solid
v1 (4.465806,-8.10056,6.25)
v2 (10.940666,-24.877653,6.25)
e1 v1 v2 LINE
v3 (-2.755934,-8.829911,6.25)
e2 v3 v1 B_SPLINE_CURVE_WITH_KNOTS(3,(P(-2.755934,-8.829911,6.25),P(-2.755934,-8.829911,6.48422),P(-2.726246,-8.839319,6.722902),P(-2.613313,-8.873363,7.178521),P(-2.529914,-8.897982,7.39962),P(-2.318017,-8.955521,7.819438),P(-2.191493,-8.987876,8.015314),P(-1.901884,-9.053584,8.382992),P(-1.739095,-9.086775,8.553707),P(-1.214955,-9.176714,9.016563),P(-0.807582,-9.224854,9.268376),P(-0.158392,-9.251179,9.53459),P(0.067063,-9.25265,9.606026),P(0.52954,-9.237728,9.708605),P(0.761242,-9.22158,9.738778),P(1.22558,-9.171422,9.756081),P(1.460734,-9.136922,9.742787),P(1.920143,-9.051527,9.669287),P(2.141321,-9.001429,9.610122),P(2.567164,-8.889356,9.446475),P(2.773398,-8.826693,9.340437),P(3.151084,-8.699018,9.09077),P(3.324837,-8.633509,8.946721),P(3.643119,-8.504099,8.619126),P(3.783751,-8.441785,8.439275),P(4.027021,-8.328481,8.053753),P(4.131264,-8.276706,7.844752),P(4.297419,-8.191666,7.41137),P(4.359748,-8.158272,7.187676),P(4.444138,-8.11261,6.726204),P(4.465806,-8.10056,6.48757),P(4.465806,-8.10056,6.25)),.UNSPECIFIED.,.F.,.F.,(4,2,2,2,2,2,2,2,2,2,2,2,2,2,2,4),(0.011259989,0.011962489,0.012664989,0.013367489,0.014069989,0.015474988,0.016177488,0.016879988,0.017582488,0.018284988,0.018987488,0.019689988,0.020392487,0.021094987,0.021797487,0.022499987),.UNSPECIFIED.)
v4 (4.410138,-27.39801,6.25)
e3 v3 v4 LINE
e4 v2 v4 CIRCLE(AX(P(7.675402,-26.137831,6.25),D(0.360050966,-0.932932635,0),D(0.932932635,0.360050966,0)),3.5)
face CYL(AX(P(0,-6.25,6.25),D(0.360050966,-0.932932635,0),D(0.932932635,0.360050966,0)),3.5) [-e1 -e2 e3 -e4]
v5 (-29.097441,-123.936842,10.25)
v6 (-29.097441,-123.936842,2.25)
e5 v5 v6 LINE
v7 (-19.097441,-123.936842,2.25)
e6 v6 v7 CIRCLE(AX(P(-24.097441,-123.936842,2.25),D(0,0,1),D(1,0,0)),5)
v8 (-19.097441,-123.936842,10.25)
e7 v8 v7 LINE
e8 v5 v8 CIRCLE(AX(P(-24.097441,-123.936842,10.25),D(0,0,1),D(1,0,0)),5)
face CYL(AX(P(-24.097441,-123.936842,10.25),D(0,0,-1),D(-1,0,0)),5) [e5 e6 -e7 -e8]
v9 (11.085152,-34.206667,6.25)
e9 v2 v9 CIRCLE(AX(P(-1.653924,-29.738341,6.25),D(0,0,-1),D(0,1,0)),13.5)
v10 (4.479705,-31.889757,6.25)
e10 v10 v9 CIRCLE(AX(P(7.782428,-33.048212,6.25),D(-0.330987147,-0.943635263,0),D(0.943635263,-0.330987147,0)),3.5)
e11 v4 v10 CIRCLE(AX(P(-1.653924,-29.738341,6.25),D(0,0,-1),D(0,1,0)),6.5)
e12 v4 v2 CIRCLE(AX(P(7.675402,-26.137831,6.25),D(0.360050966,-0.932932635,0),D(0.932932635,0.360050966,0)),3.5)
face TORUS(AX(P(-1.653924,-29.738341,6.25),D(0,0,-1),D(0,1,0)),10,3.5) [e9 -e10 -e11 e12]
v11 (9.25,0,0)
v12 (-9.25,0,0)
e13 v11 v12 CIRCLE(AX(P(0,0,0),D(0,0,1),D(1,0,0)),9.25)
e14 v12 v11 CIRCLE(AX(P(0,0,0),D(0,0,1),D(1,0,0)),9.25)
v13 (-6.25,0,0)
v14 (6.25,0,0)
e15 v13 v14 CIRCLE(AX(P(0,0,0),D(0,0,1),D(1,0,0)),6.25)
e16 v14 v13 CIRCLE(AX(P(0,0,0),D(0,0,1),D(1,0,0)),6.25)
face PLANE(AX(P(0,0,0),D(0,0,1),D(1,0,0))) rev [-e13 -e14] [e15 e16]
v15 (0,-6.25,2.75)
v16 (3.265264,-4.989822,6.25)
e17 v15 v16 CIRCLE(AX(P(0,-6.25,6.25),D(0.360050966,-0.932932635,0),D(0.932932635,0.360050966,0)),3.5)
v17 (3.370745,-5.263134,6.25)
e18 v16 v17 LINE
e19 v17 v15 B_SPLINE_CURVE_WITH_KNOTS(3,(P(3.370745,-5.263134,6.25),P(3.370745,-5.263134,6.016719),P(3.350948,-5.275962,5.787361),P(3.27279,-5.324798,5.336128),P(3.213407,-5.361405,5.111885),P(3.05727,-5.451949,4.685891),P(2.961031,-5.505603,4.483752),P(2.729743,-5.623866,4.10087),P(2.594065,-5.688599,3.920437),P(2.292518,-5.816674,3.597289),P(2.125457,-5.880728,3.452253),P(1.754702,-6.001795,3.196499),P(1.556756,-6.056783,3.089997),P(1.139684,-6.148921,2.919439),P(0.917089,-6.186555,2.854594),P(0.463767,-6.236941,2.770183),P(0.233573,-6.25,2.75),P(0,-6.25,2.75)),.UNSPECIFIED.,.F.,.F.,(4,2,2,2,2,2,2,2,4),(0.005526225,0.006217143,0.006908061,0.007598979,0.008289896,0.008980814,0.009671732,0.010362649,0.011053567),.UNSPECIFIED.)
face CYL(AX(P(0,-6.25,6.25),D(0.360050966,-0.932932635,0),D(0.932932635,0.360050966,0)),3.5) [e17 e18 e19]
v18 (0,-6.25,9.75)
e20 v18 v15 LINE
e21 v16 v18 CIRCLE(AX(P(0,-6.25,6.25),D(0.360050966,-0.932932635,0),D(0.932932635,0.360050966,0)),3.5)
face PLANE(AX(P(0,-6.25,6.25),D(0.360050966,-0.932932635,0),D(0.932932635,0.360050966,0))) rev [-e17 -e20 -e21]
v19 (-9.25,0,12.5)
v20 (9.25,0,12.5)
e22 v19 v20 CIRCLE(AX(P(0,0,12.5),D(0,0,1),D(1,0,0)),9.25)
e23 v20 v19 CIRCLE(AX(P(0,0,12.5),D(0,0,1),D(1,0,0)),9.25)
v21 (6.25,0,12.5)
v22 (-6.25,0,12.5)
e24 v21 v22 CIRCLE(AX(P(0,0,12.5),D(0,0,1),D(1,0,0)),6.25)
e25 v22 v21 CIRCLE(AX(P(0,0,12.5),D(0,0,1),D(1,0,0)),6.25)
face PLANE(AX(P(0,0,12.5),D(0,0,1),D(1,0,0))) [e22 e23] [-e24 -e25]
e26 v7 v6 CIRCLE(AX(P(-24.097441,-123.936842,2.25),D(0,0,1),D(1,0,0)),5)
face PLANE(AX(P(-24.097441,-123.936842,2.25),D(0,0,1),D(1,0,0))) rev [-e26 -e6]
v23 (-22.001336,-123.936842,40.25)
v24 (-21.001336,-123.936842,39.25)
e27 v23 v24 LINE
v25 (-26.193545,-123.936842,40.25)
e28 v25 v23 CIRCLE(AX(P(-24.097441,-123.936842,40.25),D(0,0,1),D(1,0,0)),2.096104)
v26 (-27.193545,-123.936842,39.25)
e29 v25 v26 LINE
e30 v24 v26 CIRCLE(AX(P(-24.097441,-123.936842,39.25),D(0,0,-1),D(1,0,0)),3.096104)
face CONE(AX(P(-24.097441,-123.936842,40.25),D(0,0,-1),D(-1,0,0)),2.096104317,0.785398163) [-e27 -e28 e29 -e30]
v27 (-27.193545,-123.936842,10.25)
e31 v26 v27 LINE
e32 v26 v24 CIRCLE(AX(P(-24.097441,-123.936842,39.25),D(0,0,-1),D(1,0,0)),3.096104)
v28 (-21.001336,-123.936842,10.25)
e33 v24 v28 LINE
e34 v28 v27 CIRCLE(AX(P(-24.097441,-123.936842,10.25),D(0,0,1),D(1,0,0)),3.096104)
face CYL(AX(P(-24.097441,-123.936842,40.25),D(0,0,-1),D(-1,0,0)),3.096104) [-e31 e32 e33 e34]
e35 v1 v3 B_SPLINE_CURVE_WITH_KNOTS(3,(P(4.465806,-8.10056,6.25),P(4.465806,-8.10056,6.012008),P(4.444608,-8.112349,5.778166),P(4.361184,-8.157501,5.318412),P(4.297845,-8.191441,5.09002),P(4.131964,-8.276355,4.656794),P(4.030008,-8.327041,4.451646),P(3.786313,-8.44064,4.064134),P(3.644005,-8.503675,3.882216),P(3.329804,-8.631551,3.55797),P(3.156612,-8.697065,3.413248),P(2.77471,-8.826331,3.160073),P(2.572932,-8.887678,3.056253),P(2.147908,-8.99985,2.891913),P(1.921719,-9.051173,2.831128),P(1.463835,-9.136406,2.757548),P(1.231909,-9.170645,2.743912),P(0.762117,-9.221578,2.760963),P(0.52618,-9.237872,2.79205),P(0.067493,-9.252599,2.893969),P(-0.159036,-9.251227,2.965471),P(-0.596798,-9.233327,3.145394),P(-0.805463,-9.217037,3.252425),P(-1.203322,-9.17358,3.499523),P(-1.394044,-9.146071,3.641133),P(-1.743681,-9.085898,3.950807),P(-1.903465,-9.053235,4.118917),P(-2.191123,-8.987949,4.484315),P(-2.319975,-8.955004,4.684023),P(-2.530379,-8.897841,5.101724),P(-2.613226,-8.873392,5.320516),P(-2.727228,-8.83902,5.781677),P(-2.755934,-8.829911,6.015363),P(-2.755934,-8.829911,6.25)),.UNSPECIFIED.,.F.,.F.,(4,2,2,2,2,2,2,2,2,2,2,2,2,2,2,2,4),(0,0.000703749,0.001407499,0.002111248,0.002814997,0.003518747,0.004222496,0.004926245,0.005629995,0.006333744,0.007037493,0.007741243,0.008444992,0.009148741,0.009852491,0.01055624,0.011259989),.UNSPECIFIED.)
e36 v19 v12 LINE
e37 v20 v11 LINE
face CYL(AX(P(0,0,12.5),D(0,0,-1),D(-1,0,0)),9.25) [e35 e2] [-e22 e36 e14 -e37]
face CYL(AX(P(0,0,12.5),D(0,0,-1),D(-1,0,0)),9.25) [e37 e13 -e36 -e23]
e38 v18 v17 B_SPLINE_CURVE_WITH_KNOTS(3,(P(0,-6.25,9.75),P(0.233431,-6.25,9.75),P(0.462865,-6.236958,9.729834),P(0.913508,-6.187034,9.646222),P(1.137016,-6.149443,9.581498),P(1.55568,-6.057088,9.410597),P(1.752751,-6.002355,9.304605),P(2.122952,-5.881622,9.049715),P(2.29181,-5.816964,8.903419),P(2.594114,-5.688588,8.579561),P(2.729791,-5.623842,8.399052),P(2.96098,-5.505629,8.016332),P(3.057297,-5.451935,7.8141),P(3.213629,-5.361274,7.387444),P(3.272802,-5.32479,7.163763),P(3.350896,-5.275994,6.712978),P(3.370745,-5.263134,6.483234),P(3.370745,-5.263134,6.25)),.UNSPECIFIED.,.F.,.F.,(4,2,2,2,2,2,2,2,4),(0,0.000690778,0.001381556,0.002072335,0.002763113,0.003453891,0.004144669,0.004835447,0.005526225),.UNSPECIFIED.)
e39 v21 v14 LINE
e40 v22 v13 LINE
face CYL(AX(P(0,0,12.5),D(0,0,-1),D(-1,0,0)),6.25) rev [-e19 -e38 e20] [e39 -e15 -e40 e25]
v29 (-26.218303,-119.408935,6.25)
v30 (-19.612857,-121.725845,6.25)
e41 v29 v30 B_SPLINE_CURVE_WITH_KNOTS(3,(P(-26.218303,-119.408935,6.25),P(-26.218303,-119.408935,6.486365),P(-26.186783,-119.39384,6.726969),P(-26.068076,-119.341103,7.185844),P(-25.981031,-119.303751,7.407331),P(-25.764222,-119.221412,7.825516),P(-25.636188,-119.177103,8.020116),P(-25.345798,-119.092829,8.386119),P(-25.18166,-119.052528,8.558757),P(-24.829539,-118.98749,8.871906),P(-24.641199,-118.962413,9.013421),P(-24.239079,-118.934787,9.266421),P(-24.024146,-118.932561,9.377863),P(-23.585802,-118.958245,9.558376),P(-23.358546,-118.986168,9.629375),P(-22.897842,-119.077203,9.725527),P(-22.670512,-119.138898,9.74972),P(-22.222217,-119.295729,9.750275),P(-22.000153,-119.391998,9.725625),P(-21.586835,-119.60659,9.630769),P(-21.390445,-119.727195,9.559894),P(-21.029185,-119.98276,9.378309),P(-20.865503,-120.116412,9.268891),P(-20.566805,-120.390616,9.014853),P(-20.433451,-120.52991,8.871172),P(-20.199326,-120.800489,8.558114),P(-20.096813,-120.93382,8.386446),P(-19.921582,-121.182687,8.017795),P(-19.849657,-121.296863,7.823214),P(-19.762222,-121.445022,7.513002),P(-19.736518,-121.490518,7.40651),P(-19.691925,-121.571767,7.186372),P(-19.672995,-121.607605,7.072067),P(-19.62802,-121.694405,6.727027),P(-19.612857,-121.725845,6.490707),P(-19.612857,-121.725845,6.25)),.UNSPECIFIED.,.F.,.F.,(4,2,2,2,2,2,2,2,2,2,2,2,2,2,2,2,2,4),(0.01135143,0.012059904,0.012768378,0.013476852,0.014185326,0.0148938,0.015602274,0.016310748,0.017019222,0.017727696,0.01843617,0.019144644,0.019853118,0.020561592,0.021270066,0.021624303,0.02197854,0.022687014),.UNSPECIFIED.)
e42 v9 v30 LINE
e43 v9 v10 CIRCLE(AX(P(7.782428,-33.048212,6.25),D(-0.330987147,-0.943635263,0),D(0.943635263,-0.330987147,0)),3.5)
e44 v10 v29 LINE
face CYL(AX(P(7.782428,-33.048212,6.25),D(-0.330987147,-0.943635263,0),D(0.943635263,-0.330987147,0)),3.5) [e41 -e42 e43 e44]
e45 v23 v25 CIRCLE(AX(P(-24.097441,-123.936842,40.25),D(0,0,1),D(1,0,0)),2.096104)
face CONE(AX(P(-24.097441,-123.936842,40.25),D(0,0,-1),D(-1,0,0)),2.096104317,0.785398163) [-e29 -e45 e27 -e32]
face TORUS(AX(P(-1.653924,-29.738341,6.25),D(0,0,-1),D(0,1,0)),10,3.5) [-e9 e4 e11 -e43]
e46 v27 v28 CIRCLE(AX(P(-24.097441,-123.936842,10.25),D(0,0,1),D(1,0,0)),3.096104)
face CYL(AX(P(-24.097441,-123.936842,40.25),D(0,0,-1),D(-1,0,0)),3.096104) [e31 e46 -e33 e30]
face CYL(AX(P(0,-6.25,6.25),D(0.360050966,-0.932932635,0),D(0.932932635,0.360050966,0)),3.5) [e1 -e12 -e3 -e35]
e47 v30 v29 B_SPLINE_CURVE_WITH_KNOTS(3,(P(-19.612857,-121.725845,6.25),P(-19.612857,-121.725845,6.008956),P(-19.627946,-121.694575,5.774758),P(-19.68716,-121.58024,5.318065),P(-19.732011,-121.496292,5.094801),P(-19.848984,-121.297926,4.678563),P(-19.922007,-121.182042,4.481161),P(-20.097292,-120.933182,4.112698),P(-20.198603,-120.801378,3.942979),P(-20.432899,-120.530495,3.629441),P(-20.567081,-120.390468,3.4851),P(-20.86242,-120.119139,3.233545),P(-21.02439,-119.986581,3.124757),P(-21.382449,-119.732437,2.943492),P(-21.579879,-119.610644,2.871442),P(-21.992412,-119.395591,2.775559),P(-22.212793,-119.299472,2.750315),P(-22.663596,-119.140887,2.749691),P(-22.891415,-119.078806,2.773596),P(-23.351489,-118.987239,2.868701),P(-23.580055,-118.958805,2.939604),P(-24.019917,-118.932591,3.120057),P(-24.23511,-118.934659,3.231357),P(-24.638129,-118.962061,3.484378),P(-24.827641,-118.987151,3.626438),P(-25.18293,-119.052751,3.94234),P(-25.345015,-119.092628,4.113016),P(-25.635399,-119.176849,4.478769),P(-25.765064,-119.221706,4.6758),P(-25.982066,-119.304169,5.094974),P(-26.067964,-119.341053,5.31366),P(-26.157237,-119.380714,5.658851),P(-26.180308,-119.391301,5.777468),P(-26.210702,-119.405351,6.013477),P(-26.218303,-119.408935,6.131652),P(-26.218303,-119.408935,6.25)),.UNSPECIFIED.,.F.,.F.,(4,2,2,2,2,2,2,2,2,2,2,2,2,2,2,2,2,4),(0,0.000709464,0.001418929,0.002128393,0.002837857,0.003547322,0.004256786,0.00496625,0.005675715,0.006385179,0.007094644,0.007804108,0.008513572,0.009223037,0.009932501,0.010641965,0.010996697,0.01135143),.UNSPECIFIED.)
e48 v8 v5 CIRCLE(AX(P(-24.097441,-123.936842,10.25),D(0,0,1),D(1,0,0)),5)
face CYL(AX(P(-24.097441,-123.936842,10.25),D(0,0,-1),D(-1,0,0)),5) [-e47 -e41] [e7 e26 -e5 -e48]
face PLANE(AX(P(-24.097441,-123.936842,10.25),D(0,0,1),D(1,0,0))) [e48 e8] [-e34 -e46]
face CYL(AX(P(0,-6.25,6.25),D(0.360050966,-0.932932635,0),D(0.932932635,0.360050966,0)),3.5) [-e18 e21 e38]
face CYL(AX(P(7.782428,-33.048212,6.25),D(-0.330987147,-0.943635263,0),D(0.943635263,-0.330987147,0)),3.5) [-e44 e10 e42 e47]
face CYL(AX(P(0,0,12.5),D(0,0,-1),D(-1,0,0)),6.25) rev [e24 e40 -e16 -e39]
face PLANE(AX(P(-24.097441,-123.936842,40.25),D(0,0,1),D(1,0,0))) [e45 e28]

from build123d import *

# Parameters (mm, degrees)
SKETCH1_R           = 9.25
SKETCH1_R_2         = 6.25
BOSS_EXTRUDE1_DEPTH = 12.5
SWEEP1_PROFILE_R    = 3.5
SKETCH16_R          = 5
BOSS_EXTRUDE2_DEPTH = 4
SKETCH17_R          = 3.096104317
BOSS_EXTRUDE3_DEPTH = 30
CHAMFER1_SIZE       = 1


with BuildPart() as part:
    # Sketch1 → Boss-Extrude1 (new body)
    with BuildSketch(Plane.XY):
        Circle(SKETCH1_R)
        Circle(SKETCH1_R_2, mode=Mode.SUBTRACT)
    extrude(amount=BOSS_EXTRUDE1_DEPTH)

    # Sweep1: sweep along a curve in space
    with BuildLine() as sweep1_path:
        Line((0, -6.25, 6.25), (7.675401854, -26.137831295, 6.25))
        ThreePointArc((7.782428128, -33.048212427, 6.25), (8.344876366, -29.583482004, 6.25), (7.675401854, -26.137831295, 6.25))
        Line((7.782428128, -33.048212427, 6.25), (-24.097440523, -123.936842128, 6.25))
    # Sweep1 profile (on start of the path) → Sweep1 (sweep)
    with BuildSketch(Plane(origin=(0, -6.25, 6.25), x_dir=(-0.9329326350915154, -0.36005096636615397, 0), z_dir=(0.36005096636615397, -0.9329326350915154, 0))):
        Circle(SWEEP1_PROFILE_R)
    sweep(path=sweep1_path.line)

    # Sketch16 → Boss-Extrude2 (add, symmetric)
    with BuildSketch(Plane.XY.offset(6.25)):
        with Locations((-24.097440523, -123.936842128)):
            Circle(SKETCH16_R)
    extrude(amount=BOSS_EXTRUDE2_DEPTH, both=True)

    # Sketch17 → Boss-Extrude3 (add)
    with BuildSketch(Plane.XY.offset(10.25)):
        with Locations((-24.097440523, -123.936842128)):
            Circle(SKETCH17_R)
    extrude(amount=BOSS_EXTRUDE3_DEPTH)

    # Chamfer1
    chamfer1_edges = [part.edges().sort_by_distance(p)[0] for p in [
        (-27.19354484, -123.936842128, 40.25),
    ]]
    chamfer(chamfer1_edges, length=CHAMFER1_SIZE)


solid = part.part
